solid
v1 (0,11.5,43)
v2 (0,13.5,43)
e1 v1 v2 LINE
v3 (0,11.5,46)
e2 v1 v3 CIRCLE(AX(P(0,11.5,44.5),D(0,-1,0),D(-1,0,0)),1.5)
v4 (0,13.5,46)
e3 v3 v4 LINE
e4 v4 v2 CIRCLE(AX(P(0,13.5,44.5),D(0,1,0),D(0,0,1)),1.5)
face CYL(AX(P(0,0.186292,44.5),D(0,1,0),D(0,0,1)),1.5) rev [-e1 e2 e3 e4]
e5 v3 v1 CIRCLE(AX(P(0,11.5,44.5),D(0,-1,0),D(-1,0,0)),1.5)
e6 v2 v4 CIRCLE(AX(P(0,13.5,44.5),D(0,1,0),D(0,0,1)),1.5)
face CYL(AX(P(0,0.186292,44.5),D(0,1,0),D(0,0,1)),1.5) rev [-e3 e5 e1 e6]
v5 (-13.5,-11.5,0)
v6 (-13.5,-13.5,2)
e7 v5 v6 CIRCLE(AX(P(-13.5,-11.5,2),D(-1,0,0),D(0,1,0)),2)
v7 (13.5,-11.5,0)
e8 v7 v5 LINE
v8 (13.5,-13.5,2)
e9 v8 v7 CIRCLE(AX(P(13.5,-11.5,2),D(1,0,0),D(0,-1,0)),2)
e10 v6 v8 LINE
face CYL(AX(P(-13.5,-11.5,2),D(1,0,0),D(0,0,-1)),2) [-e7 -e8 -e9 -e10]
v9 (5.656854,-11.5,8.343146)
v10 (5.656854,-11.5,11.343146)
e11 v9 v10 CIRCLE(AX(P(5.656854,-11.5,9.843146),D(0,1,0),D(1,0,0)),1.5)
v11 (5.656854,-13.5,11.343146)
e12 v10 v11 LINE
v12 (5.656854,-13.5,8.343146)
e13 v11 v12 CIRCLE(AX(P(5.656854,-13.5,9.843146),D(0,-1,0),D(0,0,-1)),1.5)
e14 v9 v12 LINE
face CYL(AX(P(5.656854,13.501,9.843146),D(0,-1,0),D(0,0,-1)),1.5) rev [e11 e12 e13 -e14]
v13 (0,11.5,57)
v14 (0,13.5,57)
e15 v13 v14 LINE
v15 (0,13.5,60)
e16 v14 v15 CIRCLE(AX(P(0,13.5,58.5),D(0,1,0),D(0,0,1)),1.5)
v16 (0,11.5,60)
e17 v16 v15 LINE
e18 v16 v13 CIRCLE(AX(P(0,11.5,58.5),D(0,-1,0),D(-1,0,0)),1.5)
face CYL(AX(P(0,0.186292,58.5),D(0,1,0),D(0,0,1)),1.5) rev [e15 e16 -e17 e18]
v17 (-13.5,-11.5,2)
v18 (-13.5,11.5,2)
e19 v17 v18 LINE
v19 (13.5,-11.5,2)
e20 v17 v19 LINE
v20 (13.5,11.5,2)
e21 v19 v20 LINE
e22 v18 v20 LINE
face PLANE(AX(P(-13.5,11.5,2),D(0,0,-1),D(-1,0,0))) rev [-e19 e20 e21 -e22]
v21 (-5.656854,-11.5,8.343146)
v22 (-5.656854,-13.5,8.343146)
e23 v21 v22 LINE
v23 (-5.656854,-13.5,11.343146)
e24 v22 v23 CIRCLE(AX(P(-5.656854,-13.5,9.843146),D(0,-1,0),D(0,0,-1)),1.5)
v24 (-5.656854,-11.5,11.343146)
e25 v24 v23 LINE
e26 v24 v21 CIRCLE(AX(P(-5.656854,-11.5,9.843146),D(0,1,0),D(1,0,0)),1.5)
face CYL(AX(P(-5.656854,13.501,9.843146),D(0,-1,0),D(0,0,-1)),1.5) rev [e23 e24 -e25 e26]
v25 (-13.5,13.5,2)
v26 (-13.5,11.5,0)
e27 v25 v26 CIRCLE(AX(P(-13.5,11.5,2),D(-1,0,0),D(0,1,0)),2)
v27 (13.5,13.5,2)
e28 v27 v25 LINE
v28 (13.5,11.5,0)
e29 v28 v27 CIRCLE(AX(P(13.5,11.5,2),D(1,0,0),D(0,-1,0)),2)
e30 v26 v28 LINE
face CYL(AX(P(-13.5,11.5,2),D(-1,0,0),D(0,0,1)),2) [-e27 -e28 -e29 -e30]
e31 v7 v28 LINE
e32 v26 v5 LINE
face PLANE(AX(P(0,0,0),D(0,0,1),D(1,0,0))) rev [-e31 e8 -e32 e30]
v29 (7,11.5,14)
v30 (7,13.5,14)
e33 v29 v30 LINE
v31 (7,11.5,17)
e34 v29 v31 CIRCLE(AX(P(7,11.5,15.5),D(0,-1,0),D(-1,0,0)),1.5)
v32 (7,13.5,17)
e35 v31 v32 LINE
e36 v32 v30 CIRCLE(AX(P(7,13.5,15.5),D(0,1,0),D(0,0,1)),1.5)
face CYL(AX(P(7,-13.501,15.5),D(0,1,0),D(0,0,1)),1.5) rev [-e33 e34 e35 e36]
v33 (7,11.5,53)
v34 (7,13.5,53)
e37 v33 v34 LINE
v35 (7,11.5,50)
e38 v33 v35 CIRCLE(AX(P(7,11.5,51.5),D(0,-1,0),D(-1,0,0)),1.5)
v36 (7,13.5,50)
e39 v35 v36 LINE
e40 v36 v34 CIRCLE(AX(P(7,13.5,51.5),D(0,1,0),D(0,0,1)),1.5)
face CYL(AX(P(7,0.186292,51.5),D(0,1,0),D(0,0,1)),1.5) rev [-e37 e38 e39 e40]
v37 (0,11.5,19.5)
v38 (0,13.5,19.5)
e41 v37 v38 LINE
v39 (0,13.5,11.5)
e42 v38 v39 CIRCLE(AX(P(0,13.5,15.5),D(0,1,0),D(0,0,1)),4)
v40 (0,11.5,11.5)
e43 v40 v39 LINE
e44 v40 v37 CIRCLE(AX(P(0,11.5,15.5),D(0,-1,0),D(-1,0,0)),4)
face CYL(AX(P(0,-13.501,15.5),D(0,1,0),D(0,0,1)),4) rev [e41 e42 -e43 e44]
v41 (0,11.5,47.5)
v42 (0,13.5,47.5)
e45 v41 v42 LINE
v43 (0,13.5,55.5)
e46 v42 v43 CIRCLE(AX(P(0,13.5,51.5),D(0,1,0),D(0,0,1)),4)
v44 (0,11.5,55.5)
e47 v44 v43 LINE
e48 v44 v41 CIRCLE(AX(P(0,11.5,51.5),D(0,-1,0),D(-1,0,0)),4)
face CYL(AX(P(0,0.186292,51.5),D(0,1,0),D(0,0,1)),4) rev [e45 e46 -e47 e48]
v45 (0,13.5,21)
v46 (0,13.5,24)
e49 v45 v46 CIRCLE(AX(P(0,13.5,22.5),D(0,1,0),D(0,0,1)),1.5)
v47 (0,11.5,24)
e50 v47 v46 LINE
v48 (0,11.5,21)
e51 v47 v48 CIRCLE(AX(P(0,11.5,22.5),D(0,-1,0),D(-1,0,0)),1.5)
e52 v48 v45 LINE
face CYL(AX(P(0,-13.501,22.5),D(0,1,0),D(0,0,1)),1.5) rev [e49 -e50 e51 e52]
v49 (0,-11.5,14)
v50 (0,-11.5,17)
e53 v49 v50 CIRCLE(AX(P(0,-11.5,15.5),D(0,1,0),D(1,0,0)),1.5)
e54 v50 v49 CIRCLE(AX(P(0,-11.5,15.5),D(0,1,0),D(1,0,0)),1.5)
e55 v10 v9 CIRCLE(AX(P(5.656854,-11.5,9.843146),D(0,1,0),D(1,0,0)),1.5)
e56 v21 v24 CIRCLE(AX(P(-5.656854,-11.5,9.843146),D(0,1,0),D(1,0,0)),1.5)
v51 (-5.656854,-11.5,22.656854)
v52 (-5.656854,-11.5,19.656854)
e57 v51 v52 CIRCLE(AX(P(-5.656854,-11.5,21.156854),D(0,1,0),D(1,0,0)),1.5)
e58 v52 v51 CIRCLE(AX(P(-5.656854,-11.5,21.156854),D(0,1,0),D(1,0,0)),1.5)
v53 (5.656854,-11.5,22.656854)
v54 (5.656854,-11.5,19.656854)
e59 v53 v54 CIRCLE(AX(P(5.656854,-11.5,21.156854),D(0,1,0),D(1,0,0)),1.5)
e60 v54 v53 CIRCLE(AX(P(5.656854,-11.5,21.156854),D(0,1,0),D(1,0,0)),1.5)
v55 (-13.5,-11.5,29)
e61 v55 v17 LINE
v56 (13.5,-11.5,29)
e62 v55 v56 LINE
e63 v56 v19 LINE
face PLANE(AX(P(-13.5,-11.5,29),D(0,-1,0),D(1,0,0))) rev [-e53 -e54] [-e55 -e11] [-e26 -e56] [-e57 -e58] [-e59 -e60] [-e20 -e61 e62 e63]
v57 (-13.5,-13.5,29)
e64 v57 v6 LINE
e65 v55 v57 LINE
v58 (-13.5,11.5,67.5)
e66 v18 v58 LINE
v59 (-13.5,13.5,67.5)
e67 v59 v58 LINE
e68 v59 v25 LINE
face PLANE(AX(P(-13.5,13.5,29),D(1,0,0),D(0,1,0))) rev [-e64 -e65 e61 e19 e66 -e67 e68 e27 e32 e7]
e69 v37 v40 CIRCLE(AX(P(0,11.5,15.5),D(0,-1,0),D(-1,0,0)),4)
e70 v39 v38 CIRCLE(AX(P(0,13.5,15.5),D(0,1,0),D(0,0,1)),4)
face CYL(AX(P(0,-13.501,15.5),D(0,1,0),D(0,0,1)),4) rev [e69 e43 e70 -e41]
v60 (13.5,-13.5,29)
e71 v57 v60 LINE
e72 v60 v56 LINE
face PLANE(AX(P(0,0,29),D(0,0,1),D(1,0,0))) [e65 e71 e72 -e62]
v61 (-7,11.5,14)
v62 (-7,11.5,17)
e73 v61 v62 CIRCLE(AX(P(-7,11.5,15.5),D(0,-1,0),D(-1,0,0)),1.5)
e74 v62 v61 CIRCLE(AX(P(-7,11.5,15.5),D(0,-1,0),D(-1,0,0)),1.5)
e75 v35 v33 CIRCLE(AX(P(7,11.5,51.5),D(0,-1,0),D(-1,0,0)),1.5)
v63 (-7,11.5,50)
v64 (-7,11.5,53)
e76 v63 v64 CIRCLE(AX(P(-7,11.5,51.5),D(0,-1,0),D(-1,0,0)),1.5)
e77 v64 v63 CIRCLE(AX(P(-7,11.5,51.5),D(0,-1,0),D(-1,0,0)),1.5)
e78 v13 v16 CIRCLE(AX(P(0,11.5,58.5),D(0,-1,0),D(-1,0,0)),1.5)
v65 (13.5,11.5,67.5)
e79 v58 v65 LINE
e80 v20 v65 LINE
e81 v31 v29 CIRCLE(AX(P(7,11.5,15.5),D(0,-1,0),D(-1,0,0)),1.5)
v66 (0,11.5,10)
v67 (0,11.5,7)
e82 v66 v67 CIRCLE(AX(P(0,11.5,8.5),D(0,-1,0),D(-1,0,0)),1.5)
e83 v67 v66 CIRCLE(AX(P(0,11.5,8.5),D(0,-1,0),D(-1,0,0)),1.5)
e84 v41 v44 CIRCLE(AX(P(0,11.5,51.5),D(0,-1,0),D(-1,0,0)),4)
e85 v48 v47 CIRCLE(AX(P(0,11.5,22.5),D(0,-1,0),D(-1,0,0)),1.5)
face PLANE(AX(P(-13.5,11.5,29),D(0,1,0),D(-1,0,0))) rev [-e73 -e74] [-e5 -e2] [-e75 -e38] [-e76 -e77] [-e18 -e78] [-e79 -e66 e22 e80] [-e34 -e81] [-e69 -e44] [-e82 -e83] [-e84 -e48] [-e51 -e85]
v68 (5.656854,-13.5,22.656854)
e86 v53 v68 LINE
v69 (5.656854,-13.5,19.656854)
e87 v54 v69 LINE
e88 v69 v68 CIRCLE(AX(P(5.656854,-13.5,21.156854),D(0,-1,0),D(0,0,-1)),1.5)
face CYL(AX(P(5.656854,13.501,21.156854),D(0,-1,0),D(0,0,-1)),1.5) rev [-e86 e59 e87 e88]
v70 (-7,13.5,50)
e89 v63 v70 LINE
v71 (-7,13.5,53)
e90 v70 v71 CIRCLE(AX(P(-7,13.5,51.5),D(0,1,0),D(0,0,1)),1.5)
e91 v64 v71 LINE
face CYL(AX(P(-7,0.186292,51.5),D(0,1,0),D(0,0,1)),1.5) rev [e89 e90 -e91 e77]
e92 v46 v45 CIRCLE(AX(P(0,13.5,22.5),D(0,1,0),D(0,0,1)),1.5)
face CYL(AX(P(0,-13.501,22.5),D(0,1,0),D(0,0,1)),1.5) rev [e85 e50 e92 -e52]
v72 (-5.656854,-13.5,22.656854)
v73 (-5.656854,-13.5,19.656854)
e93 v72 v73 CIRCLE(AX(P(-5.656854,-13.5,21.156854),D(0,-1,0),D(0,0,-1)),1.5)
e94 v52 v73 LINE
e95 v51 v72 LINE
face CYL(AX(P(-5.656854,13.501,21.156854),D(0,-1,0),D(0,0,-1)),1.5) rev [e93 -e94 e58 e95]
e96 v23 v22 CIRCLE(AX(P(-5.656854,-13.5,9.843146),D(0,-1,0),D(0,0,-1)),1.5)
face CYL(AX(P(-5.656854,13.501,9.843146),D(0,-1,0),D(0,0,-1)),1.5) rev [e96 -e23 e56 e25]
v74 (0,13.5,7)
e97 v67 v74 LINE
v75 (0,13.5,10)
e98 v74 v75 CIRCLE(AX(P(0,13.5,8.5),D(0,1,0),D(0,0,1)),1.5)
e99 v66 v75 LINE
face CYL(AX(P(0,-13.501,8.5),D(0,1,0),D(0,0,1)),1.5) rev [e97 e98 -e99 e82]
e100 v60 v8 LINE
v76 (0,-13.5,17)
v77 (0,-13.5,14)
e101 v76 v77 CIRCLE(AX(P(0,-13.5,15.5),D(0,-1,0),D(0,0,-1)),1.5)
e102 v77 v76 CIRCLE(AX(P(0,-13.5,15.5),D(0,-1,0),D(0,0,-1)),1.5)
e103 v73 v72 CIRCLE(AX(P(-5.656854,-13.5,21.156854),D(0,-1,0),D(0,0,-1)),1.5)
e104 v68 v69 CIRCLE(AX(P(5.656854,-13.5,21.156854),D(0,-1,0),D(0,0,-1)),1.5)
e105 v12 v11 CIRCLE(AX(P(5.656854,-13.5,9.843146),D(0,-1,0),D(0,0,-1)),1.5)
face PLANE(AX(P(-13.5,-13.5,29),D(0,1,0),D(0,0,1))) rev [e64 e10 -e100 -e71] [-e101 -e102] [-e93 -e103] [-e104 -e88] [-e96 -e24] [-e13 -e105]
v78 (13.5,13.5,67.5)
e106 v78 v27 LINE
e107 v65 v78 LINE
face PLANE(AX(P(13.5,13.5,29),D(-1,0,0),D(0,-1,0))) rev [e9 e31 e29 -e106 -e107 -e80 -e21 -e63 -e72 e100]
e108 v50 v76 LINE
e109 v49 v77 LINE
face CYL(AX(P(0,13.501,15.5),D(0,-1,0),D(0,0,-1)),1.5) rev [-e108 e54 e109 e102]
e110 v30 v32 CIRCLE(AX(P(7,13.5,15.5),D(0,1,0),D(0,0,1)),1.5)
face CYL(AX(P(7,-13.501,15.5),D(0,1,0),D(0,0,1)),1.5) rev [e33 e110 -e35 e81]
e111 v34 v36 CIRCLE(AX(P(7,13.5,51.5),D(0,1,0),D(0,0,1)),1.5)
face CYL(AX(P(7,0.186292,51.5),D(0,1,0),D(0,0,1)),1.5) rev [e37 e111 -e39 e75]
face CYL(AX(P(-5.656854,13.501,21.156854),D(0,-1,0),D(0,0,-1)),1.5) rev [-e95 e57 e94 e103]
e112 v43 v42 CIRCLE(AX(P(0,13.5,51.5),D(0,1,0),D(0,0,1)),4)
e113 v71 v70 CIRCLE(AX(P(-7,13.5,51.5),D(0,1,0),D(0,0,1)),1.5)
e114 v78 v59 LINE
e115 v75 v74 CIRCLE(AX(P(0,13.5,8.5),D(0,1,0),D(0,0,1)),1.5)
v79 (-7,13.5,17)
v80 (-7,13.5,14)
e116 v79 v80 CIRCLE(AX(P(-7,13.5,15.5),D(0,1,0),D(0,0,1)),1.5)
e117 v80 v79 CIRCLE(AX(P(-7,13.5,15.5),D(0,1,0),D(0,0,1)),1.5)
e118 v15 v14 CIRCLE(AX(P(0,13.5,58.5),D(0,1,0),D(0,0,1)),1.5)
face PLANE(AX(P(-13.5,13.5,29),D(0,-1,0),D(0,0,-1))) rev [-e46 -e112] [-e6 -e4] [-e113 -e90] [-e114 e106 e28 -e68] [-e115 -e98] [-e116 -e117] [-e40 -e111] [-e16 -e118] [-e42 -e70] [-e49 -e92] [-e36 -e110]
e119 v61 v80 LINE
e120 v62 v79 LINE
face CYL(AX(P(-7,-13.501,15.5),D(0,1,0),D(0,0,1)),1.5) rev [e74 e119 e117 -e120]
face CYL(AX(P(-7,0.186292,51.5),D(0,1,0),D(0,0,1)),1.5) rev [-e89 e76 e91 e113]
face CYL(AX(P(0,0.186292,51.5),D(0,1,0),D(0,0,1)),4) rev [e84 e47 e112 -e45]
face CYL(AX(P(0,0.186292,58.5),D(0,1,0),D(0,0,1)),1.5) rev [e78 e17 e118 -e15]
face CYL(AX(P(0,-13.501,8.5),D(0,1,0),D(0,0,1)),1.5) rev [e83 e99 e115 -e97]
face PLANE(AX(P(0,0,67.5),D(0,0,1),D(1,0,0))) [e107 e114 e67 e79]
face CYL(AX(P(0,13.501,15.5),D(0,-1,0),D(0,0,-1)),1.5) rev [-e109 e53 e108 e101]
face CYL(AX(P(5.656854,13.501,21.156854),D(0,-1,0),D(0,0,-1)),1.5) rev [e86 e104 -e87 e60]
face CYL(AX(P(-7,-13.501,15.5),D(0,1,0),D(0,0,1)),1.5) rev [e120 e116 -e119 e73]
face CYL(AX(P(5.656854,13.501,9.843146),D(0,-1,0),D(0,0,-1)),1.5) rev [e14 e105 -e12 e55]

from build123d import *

# Parameters (mm, degrees)
SKETCH1_W           = 27
SKETCH1_H           = 27
BOSS_EXTRUDE1_DEPTH = 29
SKETCH2_W           = 27
SKETCH2_H           = 23
CUT_EXTRUDE1_DEPTH  = 27
CUT_EXTRUDE2_REACH  = 43.86
SKETCH4_R           = 4
SKETCH4_R_2         = 1.5
CUT_EXTRUDE3_REACH  = 43.86
SKETCH5_R           = 1.5
FILLET1_R           = 2
SKETCH6_W           = 27
SKETCH6_H           = 2
BOSS_EXTRUDE2_DEPTH = 38.5
SKETCH7_R           = 4
SKETCH7_R_2         = 1.5
CUT_EXTRUDE4_DEPTH  = 2


with BuildPart() as part:
    # Sketch1 → Boss-Extrude1 (new body)
    with BuildSketch(Plane.XY):
        Rectangle(SKETCH1_W, SKETCH1_H)
    extrude(amount=BOSS_EXTRUDE1_DEPTH)

    # Sketch2 → Cut-Extrude1 (cut)
    with BuildSketch(Plane(origin=(13.5, 0, 0), x_dir=(0, 0, -1), z_dir=(1, 0, 0))):
        with Locations((-15.5, 0)):
            Rectangle(SKETCH2_W, SKETCH2_H)
    extrude(amount=-CUT_EXTRUDE1_DEPTH, mode=Mode.SUBTRACT)

    # Sketch4 → Cut-Extrude2 (cut, up to next)
    with BuildSketch(Plane(origin=(0, 13.5, 0), x_dir=(1, 0, 0), z_dir=(0, 1, 0)), mode=Mode.PRIVATE) as cut_extrude2_sk1:
        with Locations(Location((0, -15.5, 0), (0, 0, 270))):
            Circle(SKETCH4_R)
    cut_extrude2_tool1 = extrude(cut_extrude2_sk1.sketch, amount=-CUT_EXTRUDE2_REACH, mode=Mode.PRIVATE) & part.part
    # Sketch4 → Cut-Extrude2 (cut, up to next)
    with BuildSketch(Plane(origin=(0, 13.5, 0), x_dir=(1, 0, 0), z_dir=(0, 1, 0)), mode=Mode.PRIVATE) as cut_extrude2_sk2:
        with Locations(Location((0, -8.5, 0), (0, 0, 270))):
            Circle(SKETCH4_R_2)
    cut_extrude2_tool2 = extrude(cut_extrude2_sk2.sketch, amount=-CUT_EXTRUDE2_REACH, mode=Mode.PRIVATE) & part.part
    # Sketch4 → Cut-Extrude2 (cut, up to next)
    with BuildSketch(Plane(origin=(0, 13.5, 0), x_dir=(1, 0, 0), z_dir=(0, 1, 0)), mode=Mode.PRIVATE) as cut_extrude2_sk3:
        with Locations(Location((7, -15.5, 0), (0, 0, 270))):
            Circle(SKETCH4_R_2)
    cut_extrude2_tool3 = extrude(cut_extrude2_sk3.sketch, amount=-CUT_EXTRUDE2_REACH, mode=Mode.PRIVATE) & part.part
    # Sketch4 → Cut-Extrude2 (cut, up to next)
    with BuildSketch(Plane(origin=(0, 13.5, 0), x_dir=(1, 0, 0), z_dir=(0, 1, 0)), mode=Mode.PRIVATE) as cut_extrude2_sk4:
        with Locations(Location((0, -22.5, 0), (0, 0, 270))):
            Circle(SKETCH4_R_2)
    cut_extrude2_tool4 = extrude(cut_extrude2_sk4.sketch, amount=-CUT_EXTRUDE2_REACH, mode=Mode.PRIVATE) & part.part
    # Sketch4 → Cut-Extrude2 (cut, up to next)
    with BuildSketch(Plane(origin=(0, 13.5, 0), x_dir=(1, 0, 0), z_dir=(0, 1, 0)), mode=Mode.PRIVATE) as cut_extrude2_sk5:
        with Locations(Location((-7, -15.5, 0), (0, 0, 270))):
            Circle(SKETCH4_R_2)
    cut_extrude2_tool5 = extrude(cut_extrude2_sk5.sketch, amount=-CUT_EXTRUDE2_REACH, mode=Mode.PRIVATE) & part.part
    add(cut_extrude2_tool1.solids().sort_by_distance((0, 13.5, 15.5))[0], mode=Mode.SUBTRACT)
    add(cut_extrude2_tool2.solids().sort_by_distance((0, 13.5, 8.5))[0], mode=Mode.SUBTRACT)
    add(cut_extrude2_tool3.solids().sort_by_distance((7, 13.5, 15.5))[0], mode=Mode.SUBTRACT)
    add(cut_extrude2_tool4.solids().sort_by_distance((0, 13.5, 22.5))[0], mode=Mode.SUBTRACT)
    add(cut_extrude2_tool5.solids().sort_by_distance((-7, 13.5, 15.5))[0], mode=Mode.SUBTRACT)

    # Sketch5 → Cut-Extrude3 (cut, up to next)
    with BuildSketch(Plane.XZ.offset(13.5), mode=Mode.PRIVATE) as cut_extrude3_sk1:
        with Locations(Location((0, 15.5, 0), (0, 0, 270))):
            Circle(SKETCH5_R)
    cut_extrude3_tool1 = extrude(cut_extrude3_sk1.sketch, amount=-CUT_EXTRUDE3_REACH, mode=Mode.PRIVATE) & part.part
    # Sketch5 → Cut-Extrude3 (cut, up to next)
    with BuildSketch(Plane.XZ.offset(13.5), mode=Mode.PRIVATE) as cut_extrude3_sk2:
        with Locations(Location((-5.656854249, 21.156854249, 0), (0, 0, 270))):
            Circle(SKETCH5_R)
    cut_extrude3_tool2 = extrude(cut_extrude3_sk2.sketch, amount=-CUT_EXTRUDE3_REACH, mode=Mode.PRIVATE) & part.part
    # Sketch5 → Cut-Extrude3 (cut, up to next)
    with BuildSketch(Plane.XZ.offset(13.5), mode=Mode.PRIVATE) as cut_extrude3_sk3:
        with Locations(Location((5.656854249, 21.156854249, 0), (0, 0, 270))):
            Circle(SKETCH5_R)
    cut_extrude3_tool3 = extrude(cut_extrude3_sk3.sketch, amount=-CUT_EXTRUDE3_REACH, mode=Mode.PRIVATE) & part.part
    # Sketch5 → Cut-Extrude3 (cut, up to next)
    with BuildSketch(Plane.XZ.offset(13.5), mode=Mode.PRIVATE) as cut_extrude3_sk4:
        with Locations(Location((5.656854249, 9.843145751, 0), (0, 0, 270))):
            Circle(SKETCH5_R)
    cut_extrude3_tool4 = extrude(cut_extrude3_sk4.sketch, amount=-CUT_EXTRUDE3_REACH, mode=Mode.PRIVATE) & part.part
    # Sketch5 → Cut-Extrude3 (cut, up to next)
    with BuildSketch(Plane.XZ.offset(13.5), mode=Mode.PRIVATE) as cut_extrude3_sk5:
        with Locations(Location((-5.656854249, 9.843145751, 0), (0, 0, 270))):
            Circle(SKETCH5_R)
    cut_extrude3_tool5 = extrude(cut_extrude3_sk5.sketch, amount=-CUT_EXTRUDE3_REACH, mode=Mode.PRIVATE) & part.part
    add(cut_extrude3_tool1.solids().sort_by_distance((0, -13.5, 15.5))[0], mode=Mode.SUBTRACT)
    add(cut_extrude3_tool2.solids().sort_by_distance((-5.656854, -13.5, 21.156854))[0], mode=Mode.SUBTRACT)
    add(cut_extrude3_tool3.solids().sort_by_distance((5.656854, -13.5, 21.156854))[0], mode=Mode.SUBTRACT)
    add(cut_extrude3_tool4.solids().sort_by_distance((5.656854, -13.5, 9.843146))[0], mode=Mode.SUBTRACT)
    add(cut_extrude3_tool5.solids().sort_by_distance((-5.656854, -13.5, 9.843146))[0], mode=Mode.SUBTRACT)

    # Fillet1
    fillet1_edges = [part.edges().sort_by_distance(p)[0] for p in [
        (0, -13.5, 0),
        (0, 13.5, 0),
    ]]
    fillet(fillet1_edges, radius=FILLET1_R)

    # Sketch6 → Boss-Extrude2 (add)
    with BuildSketch(Plane.XY.offset(29)):
        with Locations((0, 12.5)):
            Rectangle(SKETCH6_W, SKETCH6_H)
    extrude(amount=BOSS_EXTRUDE2_DEPTH)

    # Sketch7 → Cut-Extrude4 (cut)
    with BuildSketch(Plane(origin=(0, 13.5, 0), x_dir=(1, 0, 0), z_dir=(0, 1, 0))):
        with Locations(Location((0, -51.5, 0), (0, 0, 270))):
            Circle(SKETCH7_R)
        with Locations(Location((0, -44.5, 0), (0, 0, 270))):
            Circle(SKETCH7_R_2)
        with Locations(Location((7, -51.5, 0), (0, 0, 270))):
            Circle(SKETCH7_R_2)
        with Locations(Location((0, -58.5, 0), (0, 0, 270))):
            Circle(SKETCH7_R_2)
        with Locations(Location((-7, -51.5, 0), (0, 0, 270))):
            Circle(SKETCH7_R_2)
    extrude(amount=-CUT_EXTRUDE4_DEPTH, mode=Mode.SUBTRACT)


solid = part.part
